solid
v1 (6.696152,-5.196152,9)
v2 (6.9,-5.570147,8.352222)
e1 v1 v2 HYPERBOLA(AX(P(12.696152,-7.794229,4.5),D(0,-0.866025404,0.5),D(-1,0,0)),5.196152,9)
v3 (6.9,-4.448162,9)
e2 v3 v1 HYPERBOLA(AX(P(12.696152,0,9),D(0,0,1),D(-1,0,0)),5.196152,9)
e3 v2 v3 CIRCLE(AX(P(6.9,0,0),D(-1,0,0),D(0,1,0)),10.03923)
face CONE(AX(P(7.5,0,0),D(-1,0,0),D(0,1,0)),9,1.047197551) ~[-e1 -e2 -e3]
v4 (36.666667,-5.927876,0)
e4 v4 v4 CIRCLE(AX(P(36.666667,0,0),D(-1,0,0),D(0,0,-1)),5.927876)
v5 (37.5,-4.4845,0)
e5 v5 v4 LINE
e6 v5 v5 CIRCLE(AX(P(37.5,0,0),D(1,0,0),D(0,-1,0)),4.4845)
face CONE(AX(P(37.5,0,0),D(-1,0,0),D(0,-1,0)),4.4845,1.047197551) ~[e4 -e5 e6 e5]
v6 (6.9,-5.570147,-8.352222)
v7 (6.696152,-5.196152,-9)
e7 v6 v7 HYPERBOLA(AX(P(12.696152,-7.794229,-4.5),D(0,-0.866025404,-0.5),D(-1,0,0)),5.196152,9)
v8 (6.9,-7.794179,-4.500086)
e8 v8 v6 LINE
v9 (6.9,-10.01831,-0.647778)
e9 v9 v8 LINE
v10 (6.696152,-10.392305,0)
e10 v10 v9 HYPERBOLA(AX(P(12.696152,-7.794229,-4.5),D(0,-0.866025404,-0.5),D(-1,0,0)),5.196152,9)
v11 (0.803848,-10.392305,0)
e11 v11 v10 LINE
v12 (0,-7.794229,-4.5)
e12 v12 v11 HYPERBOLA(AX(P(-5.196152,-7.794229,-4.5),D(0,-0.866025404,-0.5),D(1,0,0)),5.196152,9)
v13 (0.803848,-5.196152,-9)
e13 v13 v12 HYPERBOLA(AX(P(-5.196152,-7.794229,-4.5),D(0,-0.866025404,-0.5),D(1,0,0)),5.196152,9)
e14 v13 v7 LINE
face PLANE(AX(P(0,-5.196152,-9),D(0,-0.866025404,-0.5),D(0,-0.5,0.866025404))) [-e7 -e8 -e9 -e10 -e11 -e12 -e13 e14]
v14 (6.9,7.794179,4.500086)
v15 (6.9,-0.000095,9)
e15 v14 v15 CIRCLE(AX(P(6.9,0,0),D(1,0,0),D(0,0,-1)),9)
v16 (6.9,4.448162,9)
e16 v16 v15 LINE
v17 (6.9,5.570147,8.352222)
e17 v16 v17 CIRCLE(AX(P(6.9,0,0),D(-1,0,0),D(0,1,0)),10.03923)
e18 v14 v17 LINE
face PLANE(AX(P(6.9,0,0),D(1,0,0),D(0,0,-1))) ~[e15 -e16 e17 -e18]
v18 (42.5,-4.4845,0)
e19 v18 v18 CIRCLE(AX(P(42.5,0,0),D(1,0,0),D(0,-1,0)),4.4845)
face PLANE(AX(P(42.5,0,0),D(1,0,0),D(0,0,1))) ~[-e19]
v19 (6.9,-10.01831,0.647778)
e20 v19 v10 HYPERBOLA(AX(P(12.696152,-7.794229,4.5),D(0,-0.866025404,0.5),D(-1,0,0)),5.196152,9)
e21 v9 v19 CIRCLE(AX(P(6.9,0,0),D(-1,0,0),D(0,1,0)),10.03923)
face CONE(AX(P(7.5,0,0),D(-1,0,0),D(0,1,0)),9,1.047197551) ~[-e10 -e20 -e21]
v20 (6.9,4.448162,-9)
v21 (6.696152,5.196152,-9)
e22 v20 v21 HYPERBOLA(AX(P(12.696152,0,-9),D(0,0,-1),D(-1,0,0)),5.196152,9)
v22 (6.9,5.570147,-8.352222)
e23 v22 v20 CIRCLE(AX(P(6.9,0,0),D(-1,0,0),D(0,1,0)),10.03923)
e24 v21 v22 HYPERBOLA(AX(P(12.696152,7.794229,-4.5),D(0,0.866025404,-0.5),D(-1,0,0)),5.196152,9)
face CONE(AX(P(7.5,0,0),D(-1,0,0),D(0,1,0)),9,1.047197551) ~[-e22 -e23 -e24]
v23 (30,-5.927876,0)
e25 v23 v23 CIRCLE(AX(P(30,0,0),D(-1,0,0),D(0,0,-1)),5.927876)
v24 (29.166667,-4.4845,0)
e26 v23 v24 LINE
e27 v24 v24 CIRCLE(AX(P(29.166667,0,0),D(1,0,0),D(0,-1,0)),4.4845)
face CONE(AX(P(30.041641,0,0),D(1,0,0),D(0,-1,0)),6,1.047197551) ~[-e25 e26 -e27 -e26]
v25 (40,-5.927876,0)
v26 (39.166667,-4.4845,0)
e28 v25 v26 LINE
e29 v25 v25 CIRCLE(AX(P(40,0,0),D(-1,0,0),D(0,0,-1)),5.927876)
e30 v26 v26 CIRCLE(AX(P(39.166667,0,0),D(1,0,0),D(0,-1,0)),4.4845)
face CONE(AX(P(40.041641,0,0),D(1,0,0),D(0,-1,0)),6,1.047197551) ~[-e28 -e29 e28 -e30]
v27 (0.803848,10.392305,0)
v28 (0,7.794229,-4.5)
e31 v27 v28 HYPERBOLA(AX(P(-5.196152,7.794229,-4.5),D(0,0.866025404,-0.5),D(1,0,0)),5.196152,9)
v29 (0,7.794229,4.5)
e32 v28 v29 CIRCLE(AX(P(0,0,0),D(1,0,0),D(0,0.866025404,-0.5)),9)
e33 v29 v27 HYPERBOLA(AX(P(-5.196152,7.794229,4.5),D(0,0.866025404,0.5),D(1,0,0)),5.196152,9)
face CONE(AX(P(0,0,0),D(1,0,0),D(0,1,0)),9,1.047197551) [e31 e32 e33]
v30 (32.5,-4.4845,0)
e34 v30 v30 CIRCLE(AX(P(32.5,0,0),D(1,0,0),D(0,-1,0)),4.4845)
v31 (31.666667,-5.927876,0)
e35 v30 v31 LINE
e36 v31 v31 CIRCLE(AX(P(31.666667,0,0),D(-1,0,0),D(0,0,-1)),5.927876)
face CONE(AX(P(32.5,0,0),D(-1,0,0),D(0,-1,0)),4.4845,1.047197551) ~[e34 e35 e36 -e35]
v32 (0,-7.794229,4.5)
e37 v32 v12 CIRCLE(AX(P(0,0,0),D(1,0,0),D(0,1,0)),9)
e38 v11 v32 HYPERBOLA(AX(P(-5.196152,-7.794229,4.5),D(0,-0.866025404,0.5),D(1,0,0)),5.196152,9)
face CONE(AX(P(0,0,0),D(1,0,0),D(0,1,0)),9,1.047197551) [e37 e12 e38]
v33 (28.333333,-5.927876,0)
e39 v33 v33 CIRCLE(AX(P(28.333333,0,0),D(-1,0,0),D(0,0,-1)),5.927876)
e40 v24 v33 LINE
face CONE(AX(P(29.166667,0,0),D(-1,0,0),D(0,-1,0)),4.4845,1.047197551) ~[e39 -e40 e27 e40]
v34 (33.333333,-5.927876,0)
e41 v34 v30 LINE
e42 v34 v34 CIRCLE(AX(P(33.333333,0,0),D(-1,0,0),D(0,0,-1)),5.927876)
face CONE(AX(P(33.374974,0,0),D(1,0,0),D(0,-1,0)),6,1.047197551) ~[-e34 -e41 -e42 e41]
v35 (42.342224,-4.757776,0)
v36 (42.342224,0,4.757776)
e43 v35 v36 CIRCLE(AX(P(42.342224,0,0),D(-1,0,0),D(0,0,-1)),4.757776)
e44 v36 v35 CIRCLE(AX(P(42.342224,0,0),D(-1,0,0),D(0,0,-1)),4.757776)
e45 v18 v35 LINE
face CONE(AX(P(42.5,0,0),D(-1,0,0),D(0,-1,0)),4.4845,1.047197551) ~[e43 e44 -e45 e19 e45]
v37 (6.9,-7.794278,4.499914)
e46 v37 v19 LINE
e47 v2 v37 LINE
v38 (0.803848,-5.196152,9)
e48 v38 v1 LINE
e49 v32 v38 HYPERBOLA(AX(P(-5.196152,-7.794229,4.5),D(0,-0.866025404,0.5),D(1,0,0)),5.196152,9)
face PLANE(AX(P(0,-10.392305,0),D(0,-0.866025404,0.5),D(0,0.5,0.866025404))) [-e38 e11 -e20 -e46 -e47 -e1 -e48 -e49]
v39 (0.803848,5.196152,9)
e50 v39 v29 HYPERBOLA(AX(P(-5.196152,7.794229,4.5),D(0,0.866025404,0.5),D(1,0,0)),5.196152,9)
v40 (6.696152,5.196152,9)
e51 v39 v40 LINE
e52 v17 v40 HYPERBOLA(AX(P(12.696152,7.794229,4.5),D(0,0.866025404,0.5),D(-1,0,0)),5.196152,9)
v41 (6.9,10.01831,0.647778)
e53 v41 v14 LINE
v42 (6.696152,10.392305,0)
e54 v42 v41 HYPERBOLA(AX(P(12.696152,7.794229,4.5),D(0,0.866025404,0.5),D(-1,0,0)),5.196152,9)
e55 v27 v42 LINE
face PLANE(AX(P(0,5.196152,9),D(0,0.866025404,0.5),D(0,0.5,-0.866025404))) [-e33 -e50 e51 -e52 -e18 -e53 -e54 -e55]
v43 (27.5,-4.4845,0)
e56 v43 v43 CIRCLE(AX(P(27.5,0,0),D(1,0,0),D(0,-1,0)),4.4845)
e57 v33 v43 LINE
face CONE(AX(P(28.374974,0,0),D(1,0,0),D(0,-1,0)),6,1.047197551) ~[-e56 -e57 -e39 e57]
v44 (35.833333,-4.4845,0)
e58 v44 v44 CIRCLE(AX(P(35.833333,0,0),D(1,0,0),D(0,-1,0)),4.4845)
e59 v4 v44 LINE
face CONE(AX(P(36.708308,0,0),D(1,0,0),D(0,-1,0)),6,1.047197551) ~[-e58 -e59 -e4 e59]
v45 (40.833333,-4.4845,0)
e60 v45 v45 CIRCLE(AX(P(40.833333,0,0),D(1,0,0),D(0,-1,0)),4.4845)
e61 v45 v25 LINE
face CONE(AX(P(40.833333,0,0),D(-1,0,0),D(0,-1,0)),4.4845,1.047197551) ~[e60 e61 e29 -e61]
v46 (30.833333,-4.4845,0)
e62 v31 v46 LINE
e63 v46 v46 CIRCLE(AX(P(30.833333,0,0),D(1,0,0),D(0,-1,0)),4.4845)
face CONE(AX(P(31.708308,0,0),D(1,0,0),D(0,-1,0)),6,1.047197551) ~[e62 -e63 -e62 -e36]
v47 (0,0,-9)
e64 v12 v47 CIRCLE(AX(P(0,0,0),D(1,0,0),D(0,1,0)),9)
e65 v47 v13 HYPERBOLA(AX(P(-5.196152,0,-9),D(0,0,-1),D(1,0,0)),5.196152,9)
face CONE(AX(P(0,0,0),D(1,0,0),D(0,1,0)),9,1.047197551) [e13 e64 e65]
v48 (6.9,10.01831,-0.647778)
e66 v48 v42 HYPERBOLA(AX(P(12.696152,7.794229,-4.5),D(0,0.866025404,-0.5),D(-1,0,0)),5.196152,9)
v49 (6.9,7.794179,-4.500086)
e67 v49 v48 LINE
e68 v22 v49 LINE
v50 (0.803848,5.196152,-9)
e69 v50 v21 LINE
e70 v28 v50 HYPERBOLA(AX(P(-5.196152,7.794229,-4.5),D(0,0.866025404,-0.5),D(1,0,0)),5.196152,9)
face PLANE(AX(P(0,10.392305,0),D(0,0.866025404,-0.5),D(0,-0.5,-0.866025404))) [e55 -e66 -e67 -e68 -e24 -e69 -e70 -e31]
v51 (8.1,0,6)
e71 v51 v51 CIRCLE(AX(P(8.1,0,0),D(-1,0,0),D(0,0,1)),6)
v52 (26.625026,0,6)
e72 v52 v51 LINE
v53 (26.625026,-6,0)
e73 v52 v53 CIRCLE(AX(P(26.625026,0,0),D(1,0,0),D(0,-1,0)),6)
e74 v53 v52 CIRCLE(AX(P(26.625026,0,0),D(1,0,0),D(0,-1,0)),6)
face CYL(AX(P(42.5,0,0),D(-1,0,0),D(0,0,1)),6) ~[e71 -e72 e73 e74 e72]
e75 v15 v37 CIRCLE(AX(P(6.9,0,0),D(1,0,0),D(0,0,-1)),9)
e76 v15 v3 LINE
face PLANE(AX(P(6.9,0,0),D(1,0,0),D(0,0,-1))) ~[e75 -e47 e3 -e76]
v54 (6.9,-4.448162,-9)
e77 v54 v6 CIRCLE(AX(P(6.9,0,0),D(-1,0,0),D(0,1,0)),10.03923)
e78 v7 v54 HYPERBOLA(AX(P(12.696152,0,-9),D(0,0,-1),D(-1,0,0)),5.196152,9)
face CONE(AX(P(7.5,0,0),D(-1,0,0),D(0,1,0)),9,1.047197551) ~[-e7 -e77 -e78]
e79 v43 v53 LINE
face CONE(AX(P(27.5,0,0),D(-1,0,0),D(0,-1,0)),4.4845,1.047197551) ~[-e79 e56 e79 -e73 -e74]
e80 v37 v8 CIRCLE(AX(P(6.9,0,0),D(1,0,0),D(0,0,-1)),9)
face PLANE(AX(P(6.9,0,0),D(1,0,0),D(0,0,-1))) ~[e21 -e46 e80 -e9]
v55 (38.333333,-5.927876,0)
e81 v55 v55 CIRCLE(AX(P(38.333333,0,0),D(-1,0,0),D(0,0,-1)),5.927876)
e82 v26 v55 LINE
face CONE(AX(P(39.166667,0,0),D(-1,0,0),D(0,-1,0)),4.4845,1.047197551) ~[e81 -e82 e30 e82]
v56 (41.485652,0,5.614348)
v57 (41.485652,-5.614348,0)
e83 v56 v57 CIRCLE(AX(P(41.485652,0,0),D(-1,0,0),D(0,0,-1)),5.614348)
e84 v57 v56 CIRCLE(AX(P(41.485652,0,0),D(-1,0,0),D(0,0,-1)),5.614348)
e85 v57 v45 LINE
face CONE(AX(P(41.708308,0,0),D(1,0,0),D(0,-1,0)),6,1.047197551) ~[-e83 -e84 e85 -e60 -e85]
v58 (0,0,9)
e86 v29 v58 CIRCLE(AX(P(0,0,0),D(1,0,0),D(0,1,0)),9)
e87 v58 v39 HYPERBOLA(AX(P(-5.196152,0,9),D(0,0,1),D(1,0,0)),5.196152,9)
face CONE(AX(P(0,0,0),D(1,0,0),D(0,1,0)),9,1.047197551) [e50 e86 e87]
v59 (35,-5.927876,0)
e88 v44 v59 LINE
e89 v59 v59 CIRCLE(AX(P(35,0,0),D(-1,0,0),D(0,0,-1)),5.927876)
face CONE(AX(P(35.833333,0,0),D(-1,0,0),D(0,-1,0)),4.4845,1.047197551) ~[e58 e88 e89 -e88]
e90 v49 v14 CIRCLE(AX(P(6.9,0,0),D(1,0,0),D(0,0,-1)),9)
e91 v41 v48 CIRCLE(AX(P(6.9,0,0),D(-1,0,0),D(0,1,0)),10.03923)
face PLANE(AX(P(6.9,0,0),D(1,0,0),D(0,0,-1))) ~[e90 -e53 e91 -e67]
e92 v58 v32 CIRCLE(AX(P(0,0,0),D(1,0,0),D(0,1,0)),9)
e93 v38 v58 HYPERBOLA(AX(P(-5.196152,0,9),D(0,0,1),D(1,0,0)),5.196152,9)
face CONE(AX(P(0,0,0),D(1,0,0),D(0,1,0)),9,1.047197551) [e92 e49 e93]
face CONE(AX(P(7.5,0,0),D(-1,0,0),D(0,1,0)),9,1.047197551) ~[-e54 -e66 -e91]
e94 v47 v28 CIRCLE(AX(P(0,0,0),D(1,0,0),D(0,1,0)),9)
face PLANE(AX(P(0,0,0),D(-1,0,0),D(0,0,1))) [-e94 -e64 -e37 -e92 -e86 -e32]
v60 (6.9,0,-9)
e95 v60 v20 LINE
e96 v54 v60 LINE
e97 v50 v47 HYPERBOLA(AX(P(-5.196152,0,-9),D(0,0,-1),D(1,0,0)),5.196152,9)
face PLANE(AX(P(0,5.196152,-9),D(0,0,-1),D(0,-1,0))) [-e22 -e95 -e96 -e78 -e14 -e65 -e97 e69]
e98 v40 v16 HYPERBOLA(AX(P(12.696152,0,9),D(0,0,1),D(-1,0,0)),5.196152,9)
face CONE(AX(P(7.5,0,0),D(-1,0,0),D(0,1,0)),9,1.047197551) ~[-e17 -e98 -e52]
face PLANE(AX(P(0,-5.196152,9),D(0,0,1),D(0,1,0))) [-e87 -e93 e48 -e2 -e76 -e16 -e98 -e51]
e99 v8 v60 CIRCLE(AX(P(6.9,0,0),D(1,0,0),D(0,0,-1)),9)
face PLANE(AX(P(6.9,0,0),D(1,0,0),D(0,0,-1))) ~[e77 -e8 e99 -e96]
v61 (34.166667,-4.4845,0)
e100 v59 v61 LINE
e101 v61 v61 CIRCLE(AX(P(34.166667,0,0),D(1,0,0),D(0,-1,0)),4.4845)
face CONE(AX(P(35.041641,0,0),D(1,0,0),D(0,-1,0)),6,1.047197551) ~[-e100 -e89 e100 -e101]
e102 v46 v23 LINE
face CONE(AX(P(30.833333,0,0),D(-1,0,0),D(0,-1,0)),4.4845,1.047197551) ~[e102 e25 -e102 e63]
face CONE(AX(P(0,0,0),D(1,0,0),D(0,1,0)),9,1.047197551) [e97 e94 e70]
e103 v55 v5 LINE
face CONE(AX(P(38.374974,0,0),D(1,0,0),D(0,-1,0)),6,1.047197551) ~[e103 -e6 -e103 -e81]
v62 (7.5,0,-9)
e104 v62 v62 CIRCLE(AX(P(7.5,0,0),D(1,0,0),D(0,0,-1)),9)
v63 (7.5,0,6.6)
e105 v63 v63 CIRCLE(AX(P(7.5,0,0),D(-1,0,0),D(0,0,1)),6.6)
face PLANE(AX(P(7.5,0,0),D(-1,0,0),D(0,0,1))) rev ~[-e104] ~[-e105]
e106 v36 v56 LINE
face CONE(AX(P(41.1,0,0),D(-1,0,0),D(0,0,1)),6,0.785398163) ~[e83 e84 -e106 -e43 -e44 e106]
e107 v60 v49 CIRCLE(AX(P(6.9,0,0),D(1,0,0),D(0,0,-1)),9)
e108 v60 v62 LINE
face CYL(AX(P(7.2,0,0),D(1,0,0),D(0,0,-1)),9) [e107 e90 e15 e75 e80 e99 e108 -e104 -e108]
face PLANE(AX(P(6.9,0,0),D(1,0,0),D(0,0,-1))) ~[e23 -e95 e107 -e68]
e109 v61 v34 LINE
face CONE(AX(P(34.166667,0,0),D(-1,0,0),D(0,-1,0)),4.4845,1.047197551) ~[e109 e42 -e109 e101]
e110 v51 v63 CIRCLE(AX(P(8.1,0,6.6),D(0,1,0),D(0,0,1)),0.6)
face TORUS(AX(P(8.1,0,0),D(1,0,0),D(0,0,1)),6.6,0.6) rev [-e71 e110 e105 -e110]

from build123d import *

# Parameters (mm, degrees)
EXTRUDE_364_DEPTH      = 7.5
SKETCH_4_W             = 0.6
SKETCH_4_H             = 11.392304845
CHAMFER_2049_SIZE      = 1.4
FILLET_2094_R          = 0.6
PATTERN_LINEAR_1_COUNT = 10
PATTERN_LINEAR_1_PITCH = 1.666666667


with BuildPart() as part:
    # 草图1 → Extrude 364 (new body)
    with BuildSketch(Plane(origin=(0, 0, 0), x_dir=(0, 0, -1), z_dir=(1, 0, 0))):
        Polygon((9, 5.196152423), (9, -5.196152423), (0, -10.392304845), (-9, -5.196152423), (-9, 5.196152423), (0, 10.392304845), align=None)
    extrude(amount=EXTRUDE_364_DEPTH)

    # 草图2 → 凸台-旋转1 (revolve)
    with BuildSketch(Plane.XY, mode=Mode.PRIVATE) as revolve_1_sk:
        Polygon((0, 0), (42.5, 0), (42.5, 4.4845), (42.5, 6), (7.791693541, 6), (0, 6), align=None)
    revolve(revolve_1_sk.sketch.rotate(Axis((0, 0, 0), (1, 0, 0)), 90), axis=Axis((0, 0, 0), (1, 0, 0)))

    # 草图3 → 切除-旋转1 (revolve, cut)
    with BuildSketch(Plane.XY):
        Polygon((0, 9), (3.690598923, 15.392304845), (3.690598923, 20.392304845), (-10, 20.392304845), (-10, 9), align=None)
    revolve(axis=Axis((0, 0, 0), (1, 0, 0)), mode=Mode.SUBTRACT)

    # 草图5 → 切除-旋转2 (revolve, cut)
    with BuildSketch(Plane.XY):
        Polygon((7.5, 9), (3.809401077, 15.392304845), (3.809401077, 20.392304845), (13.809401077, 20.392304845), (13.809401077, 9), align=None)
    revolve(axis=Axis((0, 0, 0), (1, 0, 0)), mode=Mode.SUBTRACT)

    # 草图4 → 切除-旋转3 (revolve, cut)
    with BuildSketch(Plane.XY, mode=Mode.PRIVATE) as cut_revolve_3_sk:
        with Locations((7.2, 14.696152423)):
            Rectangle(SKETCH_4_W, SKETCH_4_H)
    revolve(cut_revolve_3_sk.sketch.rotate(Axis((0, 0, 0), (1, 0, 0)), 270), axis=Axis((0, 0, 0), (1, 0, 0)), mode=Mode.SUBTRACT)

    # Chamfer 2049
    chamfer_2049_edges = [part.edges().sort_by_distance(p)[0] for p in [
        (42.5, 0, -6),
    ]]
    chamfer(chamfer_2049_edges, length=CHAMFER_2049_SIZE)

    # Fillet 2094
    fillet_2094_edges = [part.edges().sort_by_distance(p)[0] for p in [
        (7.5, 0, -6),
    ]]
    fillet(fillet_2094_edges, radius=FILLET_2094_R)

    # 草图6 → 切除-旋转4 (revolve, cut)
    with BuildSketch(Plane.XY):
        Polygon((27.5, -4.4845), (26.625025667, -6), (26.625025667, -7.5), (28.374974333, -7.5), (28.374974333, -6), align=None)
    cut_revolve_4 = revolve(axis=Axis((-3.175, 0, 0), (1, 0, 0)), mode=Mode.SUBTRACT)

    # 阵列(线性)1: 切除-旋转4 ×10
    with Locations(*[(i * PATTERN_LINEAR_1_PITCH, 0, 0) for i in range(1, PATTERN_LINEAR_1_COUNT)]):
        add(cut_revolve_4, mode=Mode.SUBTRACT)


solid = part.part
